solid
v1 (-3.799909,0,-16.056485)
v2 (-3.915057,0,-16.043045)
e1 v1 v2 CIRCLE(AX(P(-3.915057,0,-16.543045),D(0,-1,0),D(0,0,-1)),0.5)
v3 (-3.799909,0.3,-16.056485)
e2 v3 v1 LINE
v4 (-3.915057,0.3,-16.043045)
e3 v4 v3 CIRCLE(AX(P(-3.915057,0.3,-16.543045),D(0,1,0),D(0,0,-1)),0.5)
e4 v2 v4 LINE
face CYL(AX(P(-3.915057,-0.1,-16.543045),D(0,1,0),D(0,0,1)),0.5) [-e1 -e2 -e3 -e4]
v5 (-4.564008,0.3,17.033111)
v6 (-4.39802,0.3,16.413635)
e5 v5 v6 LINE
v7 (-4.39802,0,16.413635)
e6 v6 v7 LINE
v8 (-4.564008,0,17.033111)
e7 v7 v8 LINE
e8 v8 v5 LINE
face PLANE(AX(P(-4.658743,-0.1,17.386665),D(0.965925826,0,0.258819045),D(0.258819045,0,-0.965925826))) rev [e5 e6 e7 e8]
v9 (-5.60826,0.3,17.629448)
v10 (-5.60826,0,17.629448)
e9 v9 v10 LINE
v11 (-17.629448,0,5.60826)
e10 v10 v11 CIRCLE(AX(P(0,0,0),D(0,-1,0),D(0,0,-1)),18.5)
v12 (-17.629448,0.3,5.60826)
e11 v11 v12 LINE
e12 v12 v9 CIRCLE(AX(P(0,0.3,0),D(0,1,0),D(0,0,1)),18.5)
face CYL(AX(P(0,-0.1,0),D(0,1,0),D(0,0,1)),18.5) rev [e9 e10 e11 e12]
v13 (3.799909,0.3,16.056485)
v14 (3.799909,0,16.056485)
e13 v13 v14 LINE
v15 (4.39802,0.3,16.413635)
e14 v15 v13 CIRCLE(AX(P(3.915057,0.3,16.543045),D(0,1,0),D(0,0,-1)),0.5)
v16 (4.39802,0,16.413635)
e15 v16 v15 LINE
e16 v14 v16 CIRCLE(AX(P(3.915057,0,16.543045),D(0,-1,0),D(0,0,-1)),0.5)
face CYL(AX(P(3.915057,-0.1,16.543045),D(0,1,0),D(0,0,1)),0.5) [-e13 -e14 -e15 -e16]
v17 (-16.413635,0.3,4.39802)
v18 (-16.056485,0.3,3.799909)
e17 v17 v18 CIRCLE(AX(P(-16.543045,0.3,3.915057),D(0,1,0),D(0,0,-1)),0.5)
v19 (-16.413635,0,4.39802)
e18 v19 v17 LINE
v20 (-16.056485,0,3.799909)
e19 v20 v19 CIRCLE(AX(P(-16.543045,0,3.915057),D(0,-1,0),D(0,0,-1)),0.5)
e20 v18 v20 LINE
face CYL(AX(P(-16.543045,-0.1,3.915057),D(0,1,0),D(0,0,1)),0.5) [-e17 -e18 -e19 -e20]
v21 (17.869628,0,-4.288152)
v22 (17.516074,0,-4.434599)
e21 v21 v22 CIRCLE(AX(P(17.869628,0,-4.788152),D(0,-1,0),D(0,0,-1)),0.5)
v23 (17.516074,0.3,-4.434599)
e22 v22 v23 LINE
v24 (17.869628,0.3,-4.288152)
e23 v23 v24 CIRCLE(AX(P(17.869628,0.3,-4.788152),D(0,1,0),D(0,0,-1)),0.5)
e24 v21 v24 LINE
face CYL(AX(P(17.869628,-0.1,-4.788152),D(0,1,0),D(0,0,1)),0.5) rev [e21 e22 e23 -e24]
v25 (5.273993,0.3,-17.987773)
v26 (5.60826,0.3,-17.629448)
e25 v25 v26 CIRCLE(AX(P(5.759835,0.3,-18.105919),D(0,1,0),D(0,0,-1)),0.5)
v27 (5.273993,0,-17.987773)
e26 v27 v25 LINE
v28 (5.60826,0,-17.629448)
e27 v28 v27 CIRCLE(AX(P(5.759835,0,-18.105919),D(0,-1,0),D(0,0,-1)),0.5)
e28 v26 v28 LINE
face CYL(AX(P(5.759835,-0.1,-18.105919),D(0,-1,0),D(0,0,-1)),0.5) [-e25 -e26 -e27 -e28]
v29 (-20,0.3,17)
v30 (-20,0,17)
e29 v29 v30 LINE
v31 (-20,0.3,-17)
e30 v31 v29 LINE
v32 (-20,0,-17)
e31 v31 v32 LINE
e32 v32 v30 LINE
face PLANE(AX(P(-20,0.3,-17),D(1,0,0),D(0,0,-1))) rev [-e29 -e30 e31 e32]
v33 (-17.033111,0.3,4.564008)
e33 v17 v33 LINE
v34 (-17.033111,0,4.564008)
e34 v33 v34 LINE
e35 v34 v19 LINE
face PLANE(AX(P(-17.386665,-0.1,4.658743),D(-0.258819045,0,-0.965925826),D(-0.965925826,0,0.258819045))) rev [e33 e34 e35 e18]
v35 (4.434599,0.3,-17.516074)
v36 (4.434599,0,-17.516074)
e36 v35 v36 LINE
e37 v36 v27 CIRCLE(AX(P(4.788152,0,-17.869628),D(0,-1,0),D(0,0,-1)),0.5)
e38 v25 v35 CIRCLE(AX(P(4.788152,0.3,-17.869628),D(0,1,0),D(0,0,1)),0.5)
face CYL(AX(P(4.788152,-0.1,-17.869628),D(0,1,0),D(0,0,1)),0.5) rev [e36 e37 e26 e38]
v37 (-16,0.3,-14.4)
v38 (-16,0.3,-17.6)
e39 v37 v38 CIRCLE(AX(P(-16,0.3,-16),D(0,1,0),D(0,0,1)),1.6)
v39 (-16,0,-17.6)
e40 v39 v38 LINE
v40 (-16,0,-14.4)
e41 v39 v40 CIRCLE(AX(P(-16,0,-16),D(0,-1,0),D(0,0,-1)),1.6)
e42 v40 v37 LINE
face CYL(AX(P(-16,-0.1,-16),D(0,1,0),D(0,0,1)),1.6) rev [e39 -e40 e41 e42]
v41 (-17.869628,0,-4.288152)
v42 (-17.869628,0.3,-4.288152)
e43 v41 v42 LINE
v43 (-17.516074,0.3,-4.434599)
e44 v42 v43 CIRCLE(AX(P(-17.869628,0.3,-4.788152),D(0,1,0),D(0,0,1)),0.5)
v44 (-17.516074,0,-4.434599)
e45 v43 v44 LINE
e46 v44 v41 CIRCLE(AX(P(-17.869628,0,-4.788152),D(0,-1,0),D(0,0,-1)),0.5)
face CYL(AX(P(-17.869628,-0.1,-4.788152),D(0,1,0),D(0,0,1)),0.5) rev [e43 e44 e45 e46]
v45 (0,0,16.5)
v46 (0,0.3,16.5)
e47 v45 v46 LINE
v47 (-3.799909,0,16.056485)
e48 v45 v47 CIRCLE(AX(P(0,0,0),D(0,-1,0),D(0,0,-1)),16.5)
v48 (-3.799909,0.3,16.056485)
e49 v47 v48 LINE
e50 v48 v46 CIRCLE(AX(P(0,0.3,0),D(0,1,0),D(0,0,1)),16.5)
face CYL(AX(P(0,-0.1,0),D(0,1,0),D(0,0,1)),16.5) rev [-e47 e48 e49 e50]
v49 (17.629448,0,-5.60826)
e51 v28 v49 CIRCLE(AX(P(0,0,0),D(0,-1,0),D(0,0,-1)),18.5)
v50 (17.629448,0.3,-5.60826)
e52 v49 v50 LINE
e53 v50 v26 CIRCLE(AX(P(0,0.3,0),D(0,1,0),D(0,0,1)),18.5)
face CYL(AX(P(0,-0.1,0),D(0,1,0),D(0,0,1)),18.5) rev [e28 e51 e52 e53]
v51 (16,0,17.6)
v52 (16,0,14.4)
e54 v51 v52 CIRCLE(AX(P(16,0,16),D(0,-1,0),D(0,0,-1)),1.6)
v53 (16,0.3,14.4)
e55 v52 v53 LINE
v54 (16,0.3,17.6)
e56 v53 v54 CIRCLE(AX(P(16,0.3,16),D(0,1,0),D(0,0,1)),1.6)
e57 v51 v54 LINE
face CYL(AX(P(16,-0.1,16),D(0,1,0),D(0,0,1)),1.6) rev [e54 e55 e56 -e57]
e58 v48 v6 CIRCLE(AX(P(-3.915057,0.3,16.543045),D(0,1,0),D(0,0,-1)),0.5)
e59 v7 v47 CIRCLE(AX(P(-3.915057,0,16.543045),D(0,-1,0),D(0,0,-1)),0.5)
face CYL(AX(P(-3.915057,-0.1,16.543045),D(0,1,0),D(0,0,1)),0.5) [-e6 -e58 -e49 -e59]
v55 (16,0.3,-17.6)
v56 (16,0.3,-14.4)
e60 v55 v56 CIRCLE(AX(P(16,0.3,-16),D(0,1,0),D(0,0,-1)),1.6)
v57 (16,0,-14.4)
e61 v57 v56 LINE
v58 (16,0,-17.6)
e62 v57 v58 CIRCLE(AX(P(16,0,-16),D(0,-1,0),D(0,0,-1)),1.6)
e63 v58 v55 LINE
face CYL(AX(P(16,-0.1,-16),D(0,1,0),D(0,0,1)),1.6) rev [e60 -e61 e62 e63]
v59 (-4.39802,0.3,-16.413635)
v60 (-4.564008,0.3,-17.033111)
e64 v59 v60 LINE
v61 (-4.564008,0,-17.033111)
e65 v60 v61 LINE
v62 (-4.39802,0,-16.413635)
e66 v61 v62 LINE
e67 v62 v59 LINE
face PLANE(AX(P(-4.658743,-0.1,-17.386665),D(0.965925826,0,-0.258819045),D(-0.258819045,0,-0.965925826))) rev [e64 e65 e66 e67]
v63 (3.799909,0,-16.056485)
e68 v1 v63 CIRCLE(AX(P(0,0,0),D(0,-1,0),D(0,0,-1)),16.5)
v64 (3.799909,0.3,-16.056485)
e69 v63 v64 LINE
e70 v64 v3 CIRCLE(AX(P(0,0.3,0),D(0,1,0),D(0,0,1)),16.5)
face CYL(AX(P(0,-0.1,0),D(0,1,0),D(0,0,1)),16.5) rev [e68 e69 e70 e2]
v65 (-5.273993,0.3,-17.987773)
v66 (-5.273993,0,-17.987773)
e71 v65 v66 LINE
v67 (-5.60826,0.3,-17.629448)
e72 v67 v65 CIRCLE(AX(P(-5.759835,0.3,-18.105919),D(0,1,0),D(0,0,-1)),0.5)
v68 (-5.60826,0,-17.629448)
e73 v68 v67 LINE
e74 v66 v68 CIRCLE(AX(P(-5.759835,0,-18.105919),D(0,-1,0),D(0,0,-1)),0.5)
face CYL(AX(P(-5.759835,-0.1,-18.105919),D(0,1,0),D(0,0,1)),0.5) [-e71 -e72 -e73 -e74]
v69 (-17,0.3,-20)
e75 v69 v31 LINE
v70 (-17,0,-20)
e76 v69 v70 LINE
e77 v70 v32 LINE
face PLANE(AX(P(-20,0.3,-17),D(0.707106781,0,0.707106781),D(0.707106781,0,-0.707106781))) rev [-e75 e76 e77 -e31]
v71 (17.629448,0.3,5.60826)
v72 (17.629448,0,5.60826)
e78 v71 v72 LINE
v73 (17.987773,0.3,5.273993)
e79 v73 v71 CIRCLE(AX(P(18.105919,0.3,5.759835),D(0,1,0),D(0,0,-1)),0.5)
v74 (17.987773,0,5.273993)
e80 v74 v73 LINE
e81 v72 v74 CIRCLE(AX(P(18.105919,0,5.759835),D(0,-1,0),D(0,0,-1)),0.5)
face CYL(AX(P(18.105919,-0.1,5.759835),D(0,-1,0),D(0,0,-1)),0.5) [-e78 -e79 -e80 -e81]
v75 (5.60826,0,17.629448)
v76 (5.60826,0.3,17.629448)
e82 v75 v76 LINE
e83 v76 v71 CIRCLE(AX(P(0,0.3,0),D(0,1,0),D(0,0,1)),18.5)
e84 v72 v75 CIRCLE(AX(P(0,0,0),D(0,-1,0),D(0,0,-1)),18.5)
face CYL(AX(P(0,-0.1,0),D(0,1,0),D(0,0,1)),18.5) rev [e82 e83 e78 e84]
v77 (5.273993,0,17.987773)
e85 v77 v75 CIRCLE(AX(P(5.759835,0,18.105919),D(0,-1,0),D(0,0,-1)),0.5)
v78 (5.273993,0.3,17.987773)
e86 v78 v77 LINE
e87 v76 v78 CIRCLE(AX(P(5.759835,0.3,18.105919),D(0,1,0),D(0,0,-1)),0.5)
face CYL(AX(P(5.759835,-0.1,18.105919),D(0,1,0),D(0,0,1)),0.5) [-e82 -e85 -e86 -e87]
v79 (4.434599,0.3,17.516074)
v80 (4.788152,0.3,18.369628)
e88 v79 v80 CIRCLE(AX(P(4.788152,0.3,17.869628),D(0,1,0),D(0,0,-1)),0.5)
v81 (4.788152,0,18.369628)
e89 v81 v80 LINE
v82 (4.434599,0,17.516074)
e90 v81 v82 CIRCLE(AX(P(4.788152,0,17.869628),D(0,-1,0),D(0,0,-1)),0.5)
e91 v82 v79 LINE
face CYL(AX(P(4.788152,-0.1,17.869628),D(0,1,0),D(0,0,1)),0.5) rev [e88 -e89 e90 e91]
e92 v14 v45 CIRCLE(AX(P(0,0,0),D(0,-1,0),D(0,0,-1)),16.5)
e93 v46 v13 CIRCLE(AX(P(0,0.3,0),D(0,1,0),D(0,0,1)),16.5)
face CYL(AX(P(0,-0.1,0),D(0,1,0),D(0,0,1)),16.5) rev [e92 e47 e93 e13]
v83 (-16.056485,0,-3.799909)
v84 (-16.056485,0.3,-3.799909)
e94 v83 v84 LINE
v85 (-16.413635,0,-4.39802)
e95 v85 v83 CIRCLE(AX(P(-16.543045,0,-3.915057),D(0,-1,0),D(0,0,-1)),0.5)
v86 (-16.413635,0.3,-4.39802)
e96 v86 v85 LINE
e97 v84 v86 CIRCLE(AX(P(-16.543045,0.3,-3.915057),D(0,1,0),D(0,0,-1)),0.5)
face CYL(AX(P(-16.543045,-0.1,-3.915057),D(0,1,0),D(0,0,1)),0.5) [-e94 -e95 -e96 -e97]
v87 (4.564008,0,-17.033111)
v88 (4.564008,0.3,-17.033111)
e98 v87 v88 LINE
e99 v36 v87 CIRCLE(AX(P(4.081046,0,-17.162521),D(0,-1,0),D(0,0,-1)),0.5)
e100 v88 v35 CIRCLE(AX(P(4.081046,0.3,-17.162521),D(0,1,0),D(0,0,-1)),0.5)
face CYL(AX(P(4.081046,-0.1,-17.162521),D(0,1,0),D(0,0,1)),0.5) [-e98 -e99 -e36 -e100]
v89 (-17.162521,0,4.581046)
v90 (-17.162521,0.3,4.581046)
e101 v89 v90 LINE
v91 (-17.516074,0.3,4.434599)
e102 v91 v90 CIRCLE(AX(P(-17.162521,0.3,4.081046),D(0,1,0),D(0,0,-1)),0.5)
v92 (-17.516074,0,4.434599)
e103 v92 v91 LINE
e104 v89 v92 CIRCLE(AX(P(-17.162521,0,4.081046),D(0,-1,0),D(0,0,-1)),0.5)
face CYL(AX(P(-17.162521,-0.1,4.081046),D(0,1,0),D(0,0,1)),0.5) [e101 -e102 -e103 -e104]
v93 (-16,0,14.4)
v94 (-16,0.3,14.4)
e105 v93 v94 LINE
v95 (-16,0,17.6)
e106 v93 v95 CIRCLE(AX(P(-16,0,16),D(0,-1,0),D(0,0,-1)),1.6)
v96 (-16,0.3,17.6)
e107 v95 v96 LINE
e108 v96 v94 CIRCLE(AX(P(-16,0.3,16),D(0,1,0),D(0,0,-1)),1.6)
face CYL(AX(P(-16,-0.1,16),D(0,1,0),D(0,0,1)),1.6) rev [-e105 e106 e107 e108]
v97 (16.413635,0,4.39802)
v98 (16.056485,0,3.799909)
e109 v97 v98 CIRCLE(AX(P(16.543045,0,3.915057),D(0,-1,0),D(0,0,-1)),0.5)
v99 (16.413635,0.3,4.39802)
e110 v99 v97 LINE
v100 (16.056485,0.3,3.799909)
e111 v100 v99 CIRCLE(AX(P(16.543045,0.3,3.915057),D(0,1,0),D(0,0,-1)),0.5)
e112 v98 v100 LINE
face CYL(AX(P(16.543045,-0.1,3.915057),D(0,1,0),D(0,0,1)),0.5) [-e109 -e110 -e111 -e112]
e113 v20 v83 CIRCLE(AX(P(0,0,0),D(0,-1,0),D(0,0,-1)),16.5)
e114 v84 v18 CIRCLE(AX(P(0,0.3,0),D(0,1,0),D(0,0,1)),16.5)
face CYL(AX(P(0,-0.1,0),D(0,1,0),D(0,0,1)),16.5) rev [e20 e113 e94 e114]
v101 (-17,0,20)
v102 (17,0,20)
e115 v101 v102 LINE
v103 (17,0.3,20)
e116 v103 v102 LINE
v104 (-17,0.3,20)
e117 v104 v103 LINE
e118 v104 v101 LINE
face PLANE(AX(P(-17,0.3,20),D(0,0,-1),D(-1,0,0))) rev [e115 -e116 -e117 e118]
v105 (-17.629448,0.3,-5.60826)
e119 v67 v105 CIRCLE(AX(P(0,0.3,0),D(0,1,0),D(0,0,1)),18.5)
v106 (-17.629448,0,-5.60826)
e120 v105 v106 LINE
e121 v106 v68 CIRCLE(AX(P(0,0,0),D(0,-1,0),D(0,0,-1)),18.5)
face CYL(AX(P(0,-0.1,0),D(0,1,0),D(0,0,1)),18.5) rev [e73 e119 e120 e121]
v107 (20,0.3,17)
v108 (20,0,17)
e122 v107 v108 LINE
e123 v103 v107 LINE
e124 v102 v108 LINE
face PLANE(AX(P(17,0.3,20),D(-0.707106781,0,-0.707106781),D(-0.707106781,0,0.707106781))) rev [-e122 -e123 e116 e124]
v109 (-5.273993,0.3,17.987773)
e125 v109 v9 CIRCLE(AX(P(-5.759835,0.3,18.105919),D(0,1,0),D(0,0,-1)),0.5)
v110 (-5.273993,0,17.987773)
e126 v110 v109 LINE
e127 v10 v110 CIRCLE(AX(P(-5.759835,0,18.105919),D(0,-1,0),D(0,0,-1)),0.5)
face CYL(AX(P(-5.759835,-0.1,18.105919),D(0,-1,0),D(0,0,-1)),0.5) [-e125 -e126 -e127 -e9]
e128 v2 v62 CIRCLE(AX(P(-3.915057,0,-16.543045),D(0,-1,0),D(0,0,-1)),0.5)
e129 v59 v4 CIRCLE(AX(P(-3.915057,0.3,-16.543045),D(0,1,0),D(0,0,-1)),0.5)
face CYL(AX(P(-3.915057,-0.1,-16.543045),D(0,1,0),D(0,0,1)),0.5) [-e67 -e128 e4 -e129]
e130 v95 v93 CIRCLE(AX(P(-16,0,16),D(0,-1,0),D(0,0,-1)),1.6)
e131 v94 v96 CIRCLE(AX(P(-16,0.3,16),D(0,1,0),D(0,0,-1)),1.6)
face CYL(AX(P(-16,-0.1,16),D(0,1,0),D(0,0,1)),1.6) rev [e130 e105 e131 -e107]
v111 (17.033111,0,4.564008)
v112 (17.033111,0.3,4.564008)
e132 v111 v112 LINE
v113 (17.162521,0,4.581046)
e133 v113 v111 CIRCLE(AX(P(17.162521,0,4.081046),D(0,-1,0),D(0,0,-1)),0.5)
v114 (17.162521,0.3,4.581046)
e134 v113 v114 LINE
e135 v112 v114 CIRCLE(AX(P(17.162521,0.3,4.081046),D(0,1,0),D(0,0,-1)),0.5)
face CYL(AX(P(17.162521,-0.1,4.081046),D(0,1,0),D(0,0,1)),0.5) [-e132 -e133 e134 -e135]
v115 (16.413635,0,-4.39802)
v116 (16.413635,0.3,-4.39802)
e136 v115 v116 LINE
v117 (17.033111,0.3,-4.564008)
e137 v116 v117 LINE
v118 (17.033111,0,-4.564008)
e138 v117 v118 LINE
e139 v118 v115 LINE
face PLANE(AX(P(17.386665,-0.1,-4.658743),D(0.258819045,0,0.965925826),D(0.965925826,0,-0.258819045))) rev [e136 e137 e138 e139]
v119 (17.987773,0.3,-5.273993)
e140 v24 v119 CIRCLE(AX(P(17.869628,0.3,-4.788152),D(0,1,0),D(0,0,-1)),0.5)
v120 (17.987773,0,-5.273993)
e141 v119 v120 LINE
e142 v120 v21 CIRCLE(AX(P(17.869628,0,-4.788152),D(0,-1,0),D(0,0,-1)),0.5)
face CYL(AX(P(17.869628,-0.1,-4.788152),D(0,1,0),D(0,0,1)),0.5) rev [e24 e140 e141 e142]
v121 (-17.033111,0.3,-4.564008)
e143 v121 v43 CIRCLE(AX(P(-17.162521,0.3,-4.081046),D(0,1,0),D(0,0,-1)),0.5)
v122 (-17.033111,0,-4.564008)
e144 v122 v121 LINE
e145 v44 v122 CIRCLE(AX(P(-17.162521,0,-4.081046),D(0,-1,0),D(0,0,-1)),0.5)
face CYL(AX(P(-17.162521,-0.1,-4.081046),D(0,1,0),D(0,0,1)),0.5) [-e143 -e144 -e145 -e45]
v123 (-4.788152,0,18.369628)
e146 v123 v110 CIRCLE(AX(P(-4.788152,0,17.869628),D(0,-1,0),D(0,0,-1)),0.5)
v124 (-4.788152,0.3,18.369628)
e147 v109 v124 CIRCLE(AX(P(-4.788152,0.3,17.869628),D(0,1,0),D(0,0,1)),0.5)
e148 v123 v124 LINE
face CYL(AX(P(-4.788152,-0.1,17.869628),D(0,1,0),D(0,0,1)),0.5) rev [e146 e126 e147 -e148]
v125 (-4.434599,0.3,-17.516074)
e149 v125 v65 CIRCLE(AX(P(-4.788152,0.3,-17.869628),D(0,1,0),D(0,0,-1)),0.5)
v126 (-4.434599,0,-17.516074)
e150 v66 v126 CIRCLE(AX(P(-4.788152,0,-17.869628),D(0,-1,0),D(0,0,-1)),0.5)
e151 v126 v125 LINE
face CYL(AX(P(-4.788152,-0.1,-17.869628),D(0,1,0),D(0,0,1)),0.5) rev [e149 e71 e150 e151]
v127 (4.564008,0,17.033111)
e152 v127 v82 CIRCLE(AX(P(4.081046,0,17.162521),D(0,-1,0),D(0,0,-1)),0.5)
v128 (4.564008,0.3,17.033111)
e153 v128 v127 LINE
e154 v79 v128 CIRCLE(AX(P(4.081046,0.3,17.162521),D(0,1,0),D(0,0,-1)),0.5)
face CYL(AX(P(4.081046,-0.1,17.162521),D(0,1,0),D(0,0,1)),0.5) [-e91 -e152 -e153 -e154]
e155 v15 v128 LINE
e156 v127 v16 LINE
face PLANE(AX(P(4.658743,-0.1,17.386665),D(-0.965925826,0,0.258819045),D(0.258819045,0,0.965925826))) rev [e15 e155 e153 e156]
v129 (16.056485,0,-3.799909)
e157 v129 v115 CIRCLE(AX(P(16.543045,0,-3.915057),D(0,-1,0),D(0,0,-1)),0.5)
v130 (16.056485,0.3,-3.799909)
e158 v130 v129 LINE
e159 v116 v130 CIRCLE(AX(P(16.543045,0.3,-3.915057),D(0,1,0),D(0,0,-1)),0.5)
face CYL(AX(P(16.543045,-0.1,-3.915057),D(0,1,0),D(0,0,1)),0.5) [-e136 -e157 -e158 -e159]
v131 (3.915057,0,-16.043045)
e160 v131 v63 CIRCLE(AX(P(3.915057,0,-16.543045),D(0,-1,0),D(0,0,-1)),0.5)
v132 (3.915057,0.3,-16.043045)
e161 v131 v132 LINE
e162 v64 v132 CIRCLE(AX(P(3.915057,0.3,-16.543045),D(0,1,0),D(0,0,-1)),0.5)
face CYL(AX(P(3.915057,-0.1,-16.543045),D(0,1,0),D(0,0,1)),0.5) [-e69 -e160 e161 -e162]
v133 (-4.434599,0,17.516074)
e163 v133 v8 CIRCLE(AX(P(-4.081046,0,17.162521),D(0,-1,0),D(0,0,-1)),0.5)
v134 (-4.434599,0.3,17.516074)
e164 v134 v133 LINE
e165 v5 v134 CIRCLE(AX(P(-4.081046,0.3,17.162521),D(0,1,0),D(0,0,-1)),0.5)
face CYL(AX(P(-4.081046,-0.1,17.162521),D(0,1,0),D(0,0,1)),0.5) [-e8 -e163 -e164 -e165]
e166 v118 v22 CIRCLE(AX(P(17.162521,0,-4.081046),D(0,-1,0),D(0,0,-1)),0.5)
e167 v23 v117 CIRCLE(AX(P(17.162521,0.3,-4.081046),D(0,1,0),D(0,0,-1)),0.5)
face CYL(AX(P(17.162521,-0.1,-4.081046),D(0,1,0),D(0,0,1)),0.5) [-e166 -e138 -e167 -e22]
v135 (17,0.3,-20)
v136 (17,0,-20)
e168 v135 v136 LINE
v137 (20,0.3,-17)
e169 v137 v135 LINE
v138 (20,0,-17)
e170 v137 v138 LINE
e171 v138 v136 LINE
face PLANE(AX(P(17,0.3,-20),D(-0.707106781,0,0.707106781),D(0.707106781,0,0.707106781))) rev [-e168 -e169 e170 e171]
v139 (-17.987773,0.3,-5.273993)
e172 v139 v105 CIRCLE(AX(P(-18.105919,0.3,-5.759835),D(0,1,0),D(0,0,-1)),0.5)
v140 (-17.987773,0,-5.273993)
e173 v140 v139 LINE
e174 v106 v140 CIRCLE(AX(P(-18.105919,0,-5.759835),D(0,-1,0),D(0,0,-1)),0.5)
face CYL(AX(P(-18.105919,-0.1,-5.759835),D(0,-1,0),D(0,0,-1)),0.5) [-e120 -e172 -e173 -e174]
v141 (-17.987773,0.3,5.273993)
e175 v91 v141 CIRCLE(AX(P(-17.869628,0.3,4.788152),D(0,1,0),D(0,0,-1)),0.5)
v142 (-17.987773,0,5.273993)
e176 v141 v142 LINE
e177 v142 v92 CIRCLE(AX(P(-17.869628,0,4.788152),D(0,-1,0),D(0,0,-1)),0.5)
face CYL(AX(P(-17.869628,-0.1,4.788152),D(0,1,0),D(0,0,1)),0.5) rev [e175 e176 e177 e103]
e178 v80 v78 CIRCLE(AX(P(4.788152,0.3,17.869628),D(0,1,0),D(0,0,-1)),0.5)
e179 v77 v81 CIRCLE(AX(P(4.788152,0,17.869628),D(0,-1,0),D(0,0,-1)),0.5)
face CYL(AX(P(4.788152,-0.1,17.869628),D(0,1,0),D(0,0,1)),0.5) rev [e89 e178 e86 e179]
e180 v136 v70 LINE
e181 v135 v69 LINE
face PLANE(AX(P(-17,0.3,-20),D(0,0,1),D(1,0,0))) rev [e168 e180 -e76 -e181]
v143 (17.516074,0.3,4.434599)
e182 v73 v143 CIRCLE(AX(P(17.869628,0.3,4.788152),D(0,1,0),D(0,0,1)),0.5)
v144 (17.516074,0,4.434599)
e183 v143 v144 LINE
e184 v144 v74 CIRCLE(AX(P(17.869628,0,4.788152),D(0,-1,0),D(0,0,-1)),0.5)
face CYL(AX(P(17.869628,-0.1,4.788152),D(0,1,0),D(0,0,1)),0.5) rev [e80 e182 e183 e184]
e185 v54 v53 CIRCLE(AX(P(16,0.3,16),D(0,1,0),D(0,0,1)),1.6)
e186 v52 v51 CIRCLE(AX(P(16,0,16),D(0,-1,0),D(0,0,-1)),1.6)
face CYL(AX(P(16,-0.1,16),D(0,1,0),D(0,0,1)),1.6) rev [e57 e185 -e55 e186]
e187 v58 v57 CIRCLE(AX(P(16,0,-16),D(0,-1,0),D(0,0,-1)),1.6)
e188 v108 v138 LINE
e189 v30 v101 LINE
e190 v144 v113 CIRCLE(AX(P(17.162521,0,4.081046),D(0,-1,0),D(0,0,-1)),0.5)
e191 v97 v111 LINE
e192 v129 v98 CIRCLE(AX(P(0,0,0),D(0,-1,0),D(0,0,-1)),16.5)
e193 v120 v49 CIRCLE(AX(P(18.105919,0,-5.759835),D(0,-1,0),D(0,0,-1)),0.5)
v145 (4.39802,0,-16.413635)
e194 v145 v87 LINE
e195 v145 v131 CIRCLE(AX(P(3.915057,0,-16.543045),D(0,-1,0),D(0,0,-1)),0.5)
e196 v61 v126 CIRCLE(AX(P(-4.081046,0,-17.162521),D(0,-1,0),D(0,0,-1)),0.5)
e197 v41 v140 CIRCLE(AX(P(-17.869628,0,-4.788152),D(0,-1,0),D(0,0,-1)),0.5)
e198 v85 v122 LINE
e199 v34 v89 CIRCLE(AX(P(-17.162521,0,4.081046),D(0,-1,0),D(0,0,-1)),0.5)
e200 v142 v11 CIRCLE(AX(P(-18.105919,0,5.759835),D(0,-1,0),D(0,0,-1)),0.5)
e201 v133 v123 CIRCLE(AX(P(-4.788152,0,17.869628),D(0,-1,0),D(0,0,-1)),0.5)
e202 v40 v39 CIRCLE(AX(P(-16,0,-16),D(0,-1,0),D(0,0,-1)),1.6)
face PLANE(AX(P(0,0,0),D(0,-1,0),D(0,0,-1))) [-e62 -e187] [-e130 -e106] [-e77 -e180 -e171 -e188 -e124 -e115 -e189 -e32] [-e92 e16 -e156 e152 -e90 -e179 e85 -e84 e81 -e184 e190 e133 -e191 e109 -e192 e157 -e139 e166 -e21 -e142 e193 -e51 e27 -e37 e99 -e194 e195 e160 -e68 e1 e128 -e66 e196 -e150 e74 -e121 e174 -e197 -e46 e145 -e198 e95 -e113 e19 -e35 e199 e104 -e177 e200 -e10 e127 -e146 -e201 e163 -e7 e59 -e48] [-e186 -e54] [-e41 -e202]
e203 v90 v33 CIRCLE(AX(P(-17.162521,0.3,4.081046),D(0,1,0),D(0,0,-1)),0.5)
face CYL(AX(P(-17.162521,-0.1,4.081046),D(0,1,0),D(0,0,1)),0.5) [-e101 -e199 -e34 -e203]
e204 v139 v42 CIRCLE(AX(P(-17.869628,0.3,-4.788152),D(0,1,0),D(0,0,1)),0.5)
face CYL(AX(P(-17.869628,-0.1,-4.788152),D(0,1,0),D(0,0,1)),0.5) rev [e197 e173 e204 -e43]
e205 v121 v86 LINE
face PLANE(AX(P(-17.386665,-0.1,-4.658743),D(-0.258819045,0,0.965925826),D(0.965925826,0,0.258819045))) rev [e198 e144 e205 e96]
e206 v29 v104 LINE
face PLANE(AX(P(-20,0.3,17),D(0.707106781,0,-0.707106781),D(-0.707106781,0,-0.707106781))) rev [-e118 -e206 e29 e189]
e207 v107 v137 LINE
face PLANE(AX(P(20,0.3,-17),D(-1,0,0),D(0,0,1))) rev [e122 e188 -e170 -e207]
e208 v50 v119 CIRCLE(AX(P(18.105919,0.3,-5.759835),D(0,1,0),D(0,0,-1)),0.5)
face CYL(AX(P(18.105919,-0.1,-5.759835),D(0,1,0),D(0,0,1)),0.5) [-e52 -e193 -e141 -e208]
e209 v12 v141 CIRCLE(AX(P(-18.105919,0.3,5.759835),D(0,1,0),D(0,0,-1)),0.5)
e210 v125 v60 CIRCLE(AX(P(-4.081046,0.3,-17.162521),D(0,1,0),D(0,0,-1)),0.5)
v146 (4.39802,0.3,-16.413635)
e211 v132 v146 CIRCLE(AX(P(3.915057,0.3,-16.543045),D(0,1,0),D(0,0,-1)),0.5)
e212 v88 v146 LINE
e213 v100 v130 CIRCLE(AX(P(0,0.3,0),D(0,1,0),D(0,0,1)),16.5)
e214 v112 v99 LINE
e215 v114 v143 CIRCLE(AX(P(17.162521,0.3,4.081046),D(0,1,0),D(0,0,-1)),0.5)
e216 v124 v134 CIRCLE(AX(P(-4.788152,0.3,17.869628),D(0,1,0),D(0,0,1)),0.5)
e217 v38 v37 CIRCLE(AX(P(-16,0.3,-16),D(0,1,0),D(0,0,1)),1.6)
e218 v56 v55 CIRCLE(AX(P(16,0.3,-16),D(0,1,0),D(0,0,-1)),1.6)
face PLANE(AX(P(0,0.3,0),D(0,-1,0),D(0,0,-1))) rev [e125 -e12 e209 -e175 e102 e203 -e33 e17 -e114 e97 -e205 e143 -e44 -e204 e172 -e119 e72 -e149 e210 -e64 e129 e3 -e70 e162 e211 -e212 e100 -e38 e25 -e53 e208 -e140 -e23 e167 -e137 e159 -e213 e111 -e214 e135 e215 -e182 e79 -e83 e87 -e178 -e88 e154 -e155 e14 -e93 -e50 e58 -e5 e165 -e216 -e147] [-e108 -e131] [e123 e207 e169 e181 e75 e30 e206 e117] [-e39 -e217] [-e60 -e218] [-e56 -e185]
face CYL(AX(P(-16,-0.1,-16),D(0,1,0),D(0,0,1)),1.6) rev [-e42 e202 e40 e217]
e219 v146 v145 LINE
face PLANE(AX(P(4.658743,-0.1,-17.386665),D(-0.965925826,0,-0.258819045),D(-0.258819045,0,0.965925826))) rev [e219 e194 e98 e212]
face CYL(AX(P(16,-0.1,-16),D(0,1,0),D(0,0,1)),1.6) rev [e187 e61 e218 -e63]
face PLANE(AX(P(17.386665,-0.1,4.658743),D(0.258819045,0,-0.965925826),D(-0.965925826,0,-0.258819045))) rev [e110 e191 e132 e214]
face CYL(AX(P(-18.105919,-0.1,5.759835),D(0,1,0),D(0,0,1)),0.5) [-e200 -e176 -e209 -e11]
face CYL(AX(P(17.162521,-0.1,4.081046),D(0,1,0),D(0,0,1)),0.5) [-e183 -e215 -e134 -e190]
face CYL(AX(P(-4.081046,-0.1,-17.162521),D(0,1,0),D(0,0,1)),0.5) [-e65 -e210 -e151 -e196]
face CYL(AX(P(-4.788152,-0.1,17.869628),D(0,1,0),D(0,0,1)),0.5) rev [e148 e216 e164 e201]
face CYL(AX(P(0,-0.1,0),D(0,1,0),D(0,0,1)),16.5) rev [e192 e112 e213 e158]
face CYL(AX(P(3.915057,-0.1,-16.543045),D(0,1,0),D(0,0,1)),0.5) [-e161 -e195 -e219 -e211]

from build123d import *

# Parameters (mm, degrees)
BOSS_EXTRUDE1_DEPTH = 0.3
CUT_EXTRUDE1_DEPTH  = 0.4
SKETCH3_R           = 0.5
CUT_EXTRUDE2_DEPTH  = 0.4
FILLET1_R           = 0.5
SKETCH4_R           = 1.6
CUT_EXTRUDE3_DEPTH  = 0.4


with BuildPart() as part:
    # Sketch1 → Boss-Extrude1 (new body)
    with BuildSketch(Plane(origin=(0, 0, 0), x_dir=(1, 0, 0), z_dir=(0, 1, 0))):
        Polygon((-20, 17), (-17, 20), (17, 20), (20, 17), (20, -17), (17, -20), (-17, -20), (-20, -17), align=None)
    extrude(amount=BOSS_EXTRUDE1_DEPTH)

    # Sketch2 → Cut-Extrude1 (cut)
    with BuildSketch(Plane(origin=(0, 0.3, 0), x_dir=(1, 0, 0), z_dir=(0, 1, 0))):
        with BuildLine():
            Line((-17.386664873, 4.658742812), (-15.937776134, 4.270514244))
            ThreePointArc((-15.937776134, 4.270514244), (-16.5, 0), (-15.937776134, -4.270514244))
            Line((-15.937776134, -4.270514244), (-17.386664873, -4.658742812))
            ThreePointArc((-17.386664873, -4.658742812), (-17.616707665, -4.356838745), (-17.992498966, -4.303484744))
            ThreePointArc((-17.992498966, -4.303484744), (-13.081475452, -13.081475452), (-4.303484744, -17.992498966))
            ThreePointArc((-4.303484744, -17.992498966), (-4.356838745, -17.616707665), (-4.658742812, -17.386664873))
            Line((-4.658742812, -17.386664873), (-4.270514244, -15.937776134))
            ThreePointArc((-4.270514244, -15.937776134), (0, -16.5), (4.270514244, -15.937776134))
            Line((4.270514244, -15.937776134), (4.658742812, -17.386664873))
            ThreePointArc((4.658742812, -17.386664873), (4.356838745, -17.616707665), (4.303484744, -17.992498966))
            ThreePointArc((4.303484744, -17.992498966), (13.081475452, -13.081475452), (17.992498966, -4.303484744))
            ThreePointArc((17.992498966, -4.303484744), (17.616707665, -4.356838745), (17.386664873, -4.658742812))
            Line((17.386664873, -4.658742812), (15.937776134, -4.270514244))
            ThreePointArc((15.937776134, -4.270514244), (16.5, 0), (15.937776134, 4.270514244))
            Line((15.937776134, 4.270514244), (17.386664873, 4.658742812))
            ThreePointArc((17.386664873, 4.658742812), (17.616707665, 4.356838745), (17.992498966, 4.303484744))
            ThreePointArc((17.992498966, 4.303484744), (13.081475452, 13.081475452), (4.303484744, 17.992498966))
            ThreePointArc((4.303484744, 17.992498966), (4.356838745, 17.616707665), (4.658742812, 17.386664873))
            Line((4.658742812, 17.386664873), (4.270514244, 15.937776134))
            ThreePointArc((4.270514244, 15.937776134), (0, 16.5), (-4.270514244, 15.937776134))
            Line((-4.270514244, 15.937776134), (-4.658742812, 17.386664873))
            ThreePointArc((-4.658742812, 17.386664873), (-4.356838745, 17.616707665), (-4.303484744, 17.992498966))
            ThreePointArc((-4.303484744, 17.992498966), (-13.081475452, 13.081475452), (-17.992498966, 4.303484744))
            ThreePointArc((-17.992498966, 4.303484744), (-17.616707665, 4.356838745), (-17.386664873, 4.658742812))
        make_face()
    extrude(amount=-CUT_EXTRUDE1_DEPTH, mode=Mode.SUBTRACT)

    # Sketch3 → Cut-Extrude2 (cut)
    with BuildSketch(Plane(origin=(0, 0.3, 0), x_dir=(1, 0, 0), z_dir=(0, 1, 0))):
        with Locations((-17.869627786, 4.788152334)):
            Circle(SKETCH3_R)
        with Locations((-17.869627786, -4.788152334)):
            Circle(SKETCH3_R)
        with Locations((4.788152334, 17.869627786)):
            Circle(SKETCH3_R)
        with Locations((-4.788152334, 17.869627786)):
            Circle(SKETCH3_R)
        with Locations((17.869627786, -4.788152334)):
            Circle(SKETCH3_R)
        with Locations((17.869627786, 4.788152334)):
            Circle(SKETCH3_R)
        with Locations((-4.788152334, -17.869627786)):
            Circle(SKETCH3_R)
        with Locations((4.788152334, -17.869627786)):
            Circle(SKETCH3_R)
    extrude(amount=-CUT_EXTRUDE2_DEPTH, mode=Mode.SUBTRACT)

    # Fillet1
    fillet1_edges = [part.edges().sort_by_distance(p)[0] for p in [
        (-5.26932237, 0.15, 17.733703555),
        (17.733703555, 0.15, 5.26932237),
        (5.26932237, 0.15, -17.733703555),
        (-17.733703555, 0.15, -5.26932237),
        (-5.26932237, 0.15, -17.733703555),
        (-17.733703555, 0.15, 5.26932237),
        (5.26932237, 0.15, 17.733703555),
        (17.733703555, 0.15, -5.26932237),
        (-15.937776134, 0.15, 4.270514244),
        (-15.937776134, 0.15, -4.270514244),
        (-17.386664873, 0.15, -4.658742812),
        (-4.658742812, 0.15, -17.386664873),
        (-4.270514244, 0.15, -15.937776134),
        (4.270514244, 0.15, -15.937776134),
        (4.658742812, 0.15, -17.386664873),
        (17.386664873, 0.15, -4.658742812),
        (15.937776134, 0.15, -4.270514244),
        (15.937776134, 0.15, 4.270514244),
        (17.386664873, 0.15, 4.658742812),
        (4.658742812, 0.15, 17.386664873),
        (4.270514244, 0.15, 15.937776134),
        (-4.270514244, 0.15, 15.937776134),
        (-4.658742812, 0.15, 17.386664873),
        (-17.386664873, 0.15, 4.658742812),
    ]]
    fillet(fillet1_edges, radius=FILLET1_R)

    # Sketch4 → Cut-Extrude3 (cut)
    with BuildSketch(Plane(origin=(0, 0.3, 0), x_dir=(1, 0, 0), z_dir=(0, 1, 0))):
        with Locations(Location((-16, 16, 0), (0, 0, 270))):
            Circle(SKETCH4_R)
        with Locations(Location((16, 16, 0), (0, 0, 90))):
            Circle(SKETCH4_R)
        with Locations(Location((16, -16, 0), (0, 0, 270))):
            Circle(SKETCH4_R)
        with Locations(Location((-16, -16, 0), (0, 0, 90))):
            Circle(SKETCH4_R)
    extrude(amount=-CUT_EXTRUDE3_DEPTH, mode=Mode.SUBTRACT)


solid = part.part
